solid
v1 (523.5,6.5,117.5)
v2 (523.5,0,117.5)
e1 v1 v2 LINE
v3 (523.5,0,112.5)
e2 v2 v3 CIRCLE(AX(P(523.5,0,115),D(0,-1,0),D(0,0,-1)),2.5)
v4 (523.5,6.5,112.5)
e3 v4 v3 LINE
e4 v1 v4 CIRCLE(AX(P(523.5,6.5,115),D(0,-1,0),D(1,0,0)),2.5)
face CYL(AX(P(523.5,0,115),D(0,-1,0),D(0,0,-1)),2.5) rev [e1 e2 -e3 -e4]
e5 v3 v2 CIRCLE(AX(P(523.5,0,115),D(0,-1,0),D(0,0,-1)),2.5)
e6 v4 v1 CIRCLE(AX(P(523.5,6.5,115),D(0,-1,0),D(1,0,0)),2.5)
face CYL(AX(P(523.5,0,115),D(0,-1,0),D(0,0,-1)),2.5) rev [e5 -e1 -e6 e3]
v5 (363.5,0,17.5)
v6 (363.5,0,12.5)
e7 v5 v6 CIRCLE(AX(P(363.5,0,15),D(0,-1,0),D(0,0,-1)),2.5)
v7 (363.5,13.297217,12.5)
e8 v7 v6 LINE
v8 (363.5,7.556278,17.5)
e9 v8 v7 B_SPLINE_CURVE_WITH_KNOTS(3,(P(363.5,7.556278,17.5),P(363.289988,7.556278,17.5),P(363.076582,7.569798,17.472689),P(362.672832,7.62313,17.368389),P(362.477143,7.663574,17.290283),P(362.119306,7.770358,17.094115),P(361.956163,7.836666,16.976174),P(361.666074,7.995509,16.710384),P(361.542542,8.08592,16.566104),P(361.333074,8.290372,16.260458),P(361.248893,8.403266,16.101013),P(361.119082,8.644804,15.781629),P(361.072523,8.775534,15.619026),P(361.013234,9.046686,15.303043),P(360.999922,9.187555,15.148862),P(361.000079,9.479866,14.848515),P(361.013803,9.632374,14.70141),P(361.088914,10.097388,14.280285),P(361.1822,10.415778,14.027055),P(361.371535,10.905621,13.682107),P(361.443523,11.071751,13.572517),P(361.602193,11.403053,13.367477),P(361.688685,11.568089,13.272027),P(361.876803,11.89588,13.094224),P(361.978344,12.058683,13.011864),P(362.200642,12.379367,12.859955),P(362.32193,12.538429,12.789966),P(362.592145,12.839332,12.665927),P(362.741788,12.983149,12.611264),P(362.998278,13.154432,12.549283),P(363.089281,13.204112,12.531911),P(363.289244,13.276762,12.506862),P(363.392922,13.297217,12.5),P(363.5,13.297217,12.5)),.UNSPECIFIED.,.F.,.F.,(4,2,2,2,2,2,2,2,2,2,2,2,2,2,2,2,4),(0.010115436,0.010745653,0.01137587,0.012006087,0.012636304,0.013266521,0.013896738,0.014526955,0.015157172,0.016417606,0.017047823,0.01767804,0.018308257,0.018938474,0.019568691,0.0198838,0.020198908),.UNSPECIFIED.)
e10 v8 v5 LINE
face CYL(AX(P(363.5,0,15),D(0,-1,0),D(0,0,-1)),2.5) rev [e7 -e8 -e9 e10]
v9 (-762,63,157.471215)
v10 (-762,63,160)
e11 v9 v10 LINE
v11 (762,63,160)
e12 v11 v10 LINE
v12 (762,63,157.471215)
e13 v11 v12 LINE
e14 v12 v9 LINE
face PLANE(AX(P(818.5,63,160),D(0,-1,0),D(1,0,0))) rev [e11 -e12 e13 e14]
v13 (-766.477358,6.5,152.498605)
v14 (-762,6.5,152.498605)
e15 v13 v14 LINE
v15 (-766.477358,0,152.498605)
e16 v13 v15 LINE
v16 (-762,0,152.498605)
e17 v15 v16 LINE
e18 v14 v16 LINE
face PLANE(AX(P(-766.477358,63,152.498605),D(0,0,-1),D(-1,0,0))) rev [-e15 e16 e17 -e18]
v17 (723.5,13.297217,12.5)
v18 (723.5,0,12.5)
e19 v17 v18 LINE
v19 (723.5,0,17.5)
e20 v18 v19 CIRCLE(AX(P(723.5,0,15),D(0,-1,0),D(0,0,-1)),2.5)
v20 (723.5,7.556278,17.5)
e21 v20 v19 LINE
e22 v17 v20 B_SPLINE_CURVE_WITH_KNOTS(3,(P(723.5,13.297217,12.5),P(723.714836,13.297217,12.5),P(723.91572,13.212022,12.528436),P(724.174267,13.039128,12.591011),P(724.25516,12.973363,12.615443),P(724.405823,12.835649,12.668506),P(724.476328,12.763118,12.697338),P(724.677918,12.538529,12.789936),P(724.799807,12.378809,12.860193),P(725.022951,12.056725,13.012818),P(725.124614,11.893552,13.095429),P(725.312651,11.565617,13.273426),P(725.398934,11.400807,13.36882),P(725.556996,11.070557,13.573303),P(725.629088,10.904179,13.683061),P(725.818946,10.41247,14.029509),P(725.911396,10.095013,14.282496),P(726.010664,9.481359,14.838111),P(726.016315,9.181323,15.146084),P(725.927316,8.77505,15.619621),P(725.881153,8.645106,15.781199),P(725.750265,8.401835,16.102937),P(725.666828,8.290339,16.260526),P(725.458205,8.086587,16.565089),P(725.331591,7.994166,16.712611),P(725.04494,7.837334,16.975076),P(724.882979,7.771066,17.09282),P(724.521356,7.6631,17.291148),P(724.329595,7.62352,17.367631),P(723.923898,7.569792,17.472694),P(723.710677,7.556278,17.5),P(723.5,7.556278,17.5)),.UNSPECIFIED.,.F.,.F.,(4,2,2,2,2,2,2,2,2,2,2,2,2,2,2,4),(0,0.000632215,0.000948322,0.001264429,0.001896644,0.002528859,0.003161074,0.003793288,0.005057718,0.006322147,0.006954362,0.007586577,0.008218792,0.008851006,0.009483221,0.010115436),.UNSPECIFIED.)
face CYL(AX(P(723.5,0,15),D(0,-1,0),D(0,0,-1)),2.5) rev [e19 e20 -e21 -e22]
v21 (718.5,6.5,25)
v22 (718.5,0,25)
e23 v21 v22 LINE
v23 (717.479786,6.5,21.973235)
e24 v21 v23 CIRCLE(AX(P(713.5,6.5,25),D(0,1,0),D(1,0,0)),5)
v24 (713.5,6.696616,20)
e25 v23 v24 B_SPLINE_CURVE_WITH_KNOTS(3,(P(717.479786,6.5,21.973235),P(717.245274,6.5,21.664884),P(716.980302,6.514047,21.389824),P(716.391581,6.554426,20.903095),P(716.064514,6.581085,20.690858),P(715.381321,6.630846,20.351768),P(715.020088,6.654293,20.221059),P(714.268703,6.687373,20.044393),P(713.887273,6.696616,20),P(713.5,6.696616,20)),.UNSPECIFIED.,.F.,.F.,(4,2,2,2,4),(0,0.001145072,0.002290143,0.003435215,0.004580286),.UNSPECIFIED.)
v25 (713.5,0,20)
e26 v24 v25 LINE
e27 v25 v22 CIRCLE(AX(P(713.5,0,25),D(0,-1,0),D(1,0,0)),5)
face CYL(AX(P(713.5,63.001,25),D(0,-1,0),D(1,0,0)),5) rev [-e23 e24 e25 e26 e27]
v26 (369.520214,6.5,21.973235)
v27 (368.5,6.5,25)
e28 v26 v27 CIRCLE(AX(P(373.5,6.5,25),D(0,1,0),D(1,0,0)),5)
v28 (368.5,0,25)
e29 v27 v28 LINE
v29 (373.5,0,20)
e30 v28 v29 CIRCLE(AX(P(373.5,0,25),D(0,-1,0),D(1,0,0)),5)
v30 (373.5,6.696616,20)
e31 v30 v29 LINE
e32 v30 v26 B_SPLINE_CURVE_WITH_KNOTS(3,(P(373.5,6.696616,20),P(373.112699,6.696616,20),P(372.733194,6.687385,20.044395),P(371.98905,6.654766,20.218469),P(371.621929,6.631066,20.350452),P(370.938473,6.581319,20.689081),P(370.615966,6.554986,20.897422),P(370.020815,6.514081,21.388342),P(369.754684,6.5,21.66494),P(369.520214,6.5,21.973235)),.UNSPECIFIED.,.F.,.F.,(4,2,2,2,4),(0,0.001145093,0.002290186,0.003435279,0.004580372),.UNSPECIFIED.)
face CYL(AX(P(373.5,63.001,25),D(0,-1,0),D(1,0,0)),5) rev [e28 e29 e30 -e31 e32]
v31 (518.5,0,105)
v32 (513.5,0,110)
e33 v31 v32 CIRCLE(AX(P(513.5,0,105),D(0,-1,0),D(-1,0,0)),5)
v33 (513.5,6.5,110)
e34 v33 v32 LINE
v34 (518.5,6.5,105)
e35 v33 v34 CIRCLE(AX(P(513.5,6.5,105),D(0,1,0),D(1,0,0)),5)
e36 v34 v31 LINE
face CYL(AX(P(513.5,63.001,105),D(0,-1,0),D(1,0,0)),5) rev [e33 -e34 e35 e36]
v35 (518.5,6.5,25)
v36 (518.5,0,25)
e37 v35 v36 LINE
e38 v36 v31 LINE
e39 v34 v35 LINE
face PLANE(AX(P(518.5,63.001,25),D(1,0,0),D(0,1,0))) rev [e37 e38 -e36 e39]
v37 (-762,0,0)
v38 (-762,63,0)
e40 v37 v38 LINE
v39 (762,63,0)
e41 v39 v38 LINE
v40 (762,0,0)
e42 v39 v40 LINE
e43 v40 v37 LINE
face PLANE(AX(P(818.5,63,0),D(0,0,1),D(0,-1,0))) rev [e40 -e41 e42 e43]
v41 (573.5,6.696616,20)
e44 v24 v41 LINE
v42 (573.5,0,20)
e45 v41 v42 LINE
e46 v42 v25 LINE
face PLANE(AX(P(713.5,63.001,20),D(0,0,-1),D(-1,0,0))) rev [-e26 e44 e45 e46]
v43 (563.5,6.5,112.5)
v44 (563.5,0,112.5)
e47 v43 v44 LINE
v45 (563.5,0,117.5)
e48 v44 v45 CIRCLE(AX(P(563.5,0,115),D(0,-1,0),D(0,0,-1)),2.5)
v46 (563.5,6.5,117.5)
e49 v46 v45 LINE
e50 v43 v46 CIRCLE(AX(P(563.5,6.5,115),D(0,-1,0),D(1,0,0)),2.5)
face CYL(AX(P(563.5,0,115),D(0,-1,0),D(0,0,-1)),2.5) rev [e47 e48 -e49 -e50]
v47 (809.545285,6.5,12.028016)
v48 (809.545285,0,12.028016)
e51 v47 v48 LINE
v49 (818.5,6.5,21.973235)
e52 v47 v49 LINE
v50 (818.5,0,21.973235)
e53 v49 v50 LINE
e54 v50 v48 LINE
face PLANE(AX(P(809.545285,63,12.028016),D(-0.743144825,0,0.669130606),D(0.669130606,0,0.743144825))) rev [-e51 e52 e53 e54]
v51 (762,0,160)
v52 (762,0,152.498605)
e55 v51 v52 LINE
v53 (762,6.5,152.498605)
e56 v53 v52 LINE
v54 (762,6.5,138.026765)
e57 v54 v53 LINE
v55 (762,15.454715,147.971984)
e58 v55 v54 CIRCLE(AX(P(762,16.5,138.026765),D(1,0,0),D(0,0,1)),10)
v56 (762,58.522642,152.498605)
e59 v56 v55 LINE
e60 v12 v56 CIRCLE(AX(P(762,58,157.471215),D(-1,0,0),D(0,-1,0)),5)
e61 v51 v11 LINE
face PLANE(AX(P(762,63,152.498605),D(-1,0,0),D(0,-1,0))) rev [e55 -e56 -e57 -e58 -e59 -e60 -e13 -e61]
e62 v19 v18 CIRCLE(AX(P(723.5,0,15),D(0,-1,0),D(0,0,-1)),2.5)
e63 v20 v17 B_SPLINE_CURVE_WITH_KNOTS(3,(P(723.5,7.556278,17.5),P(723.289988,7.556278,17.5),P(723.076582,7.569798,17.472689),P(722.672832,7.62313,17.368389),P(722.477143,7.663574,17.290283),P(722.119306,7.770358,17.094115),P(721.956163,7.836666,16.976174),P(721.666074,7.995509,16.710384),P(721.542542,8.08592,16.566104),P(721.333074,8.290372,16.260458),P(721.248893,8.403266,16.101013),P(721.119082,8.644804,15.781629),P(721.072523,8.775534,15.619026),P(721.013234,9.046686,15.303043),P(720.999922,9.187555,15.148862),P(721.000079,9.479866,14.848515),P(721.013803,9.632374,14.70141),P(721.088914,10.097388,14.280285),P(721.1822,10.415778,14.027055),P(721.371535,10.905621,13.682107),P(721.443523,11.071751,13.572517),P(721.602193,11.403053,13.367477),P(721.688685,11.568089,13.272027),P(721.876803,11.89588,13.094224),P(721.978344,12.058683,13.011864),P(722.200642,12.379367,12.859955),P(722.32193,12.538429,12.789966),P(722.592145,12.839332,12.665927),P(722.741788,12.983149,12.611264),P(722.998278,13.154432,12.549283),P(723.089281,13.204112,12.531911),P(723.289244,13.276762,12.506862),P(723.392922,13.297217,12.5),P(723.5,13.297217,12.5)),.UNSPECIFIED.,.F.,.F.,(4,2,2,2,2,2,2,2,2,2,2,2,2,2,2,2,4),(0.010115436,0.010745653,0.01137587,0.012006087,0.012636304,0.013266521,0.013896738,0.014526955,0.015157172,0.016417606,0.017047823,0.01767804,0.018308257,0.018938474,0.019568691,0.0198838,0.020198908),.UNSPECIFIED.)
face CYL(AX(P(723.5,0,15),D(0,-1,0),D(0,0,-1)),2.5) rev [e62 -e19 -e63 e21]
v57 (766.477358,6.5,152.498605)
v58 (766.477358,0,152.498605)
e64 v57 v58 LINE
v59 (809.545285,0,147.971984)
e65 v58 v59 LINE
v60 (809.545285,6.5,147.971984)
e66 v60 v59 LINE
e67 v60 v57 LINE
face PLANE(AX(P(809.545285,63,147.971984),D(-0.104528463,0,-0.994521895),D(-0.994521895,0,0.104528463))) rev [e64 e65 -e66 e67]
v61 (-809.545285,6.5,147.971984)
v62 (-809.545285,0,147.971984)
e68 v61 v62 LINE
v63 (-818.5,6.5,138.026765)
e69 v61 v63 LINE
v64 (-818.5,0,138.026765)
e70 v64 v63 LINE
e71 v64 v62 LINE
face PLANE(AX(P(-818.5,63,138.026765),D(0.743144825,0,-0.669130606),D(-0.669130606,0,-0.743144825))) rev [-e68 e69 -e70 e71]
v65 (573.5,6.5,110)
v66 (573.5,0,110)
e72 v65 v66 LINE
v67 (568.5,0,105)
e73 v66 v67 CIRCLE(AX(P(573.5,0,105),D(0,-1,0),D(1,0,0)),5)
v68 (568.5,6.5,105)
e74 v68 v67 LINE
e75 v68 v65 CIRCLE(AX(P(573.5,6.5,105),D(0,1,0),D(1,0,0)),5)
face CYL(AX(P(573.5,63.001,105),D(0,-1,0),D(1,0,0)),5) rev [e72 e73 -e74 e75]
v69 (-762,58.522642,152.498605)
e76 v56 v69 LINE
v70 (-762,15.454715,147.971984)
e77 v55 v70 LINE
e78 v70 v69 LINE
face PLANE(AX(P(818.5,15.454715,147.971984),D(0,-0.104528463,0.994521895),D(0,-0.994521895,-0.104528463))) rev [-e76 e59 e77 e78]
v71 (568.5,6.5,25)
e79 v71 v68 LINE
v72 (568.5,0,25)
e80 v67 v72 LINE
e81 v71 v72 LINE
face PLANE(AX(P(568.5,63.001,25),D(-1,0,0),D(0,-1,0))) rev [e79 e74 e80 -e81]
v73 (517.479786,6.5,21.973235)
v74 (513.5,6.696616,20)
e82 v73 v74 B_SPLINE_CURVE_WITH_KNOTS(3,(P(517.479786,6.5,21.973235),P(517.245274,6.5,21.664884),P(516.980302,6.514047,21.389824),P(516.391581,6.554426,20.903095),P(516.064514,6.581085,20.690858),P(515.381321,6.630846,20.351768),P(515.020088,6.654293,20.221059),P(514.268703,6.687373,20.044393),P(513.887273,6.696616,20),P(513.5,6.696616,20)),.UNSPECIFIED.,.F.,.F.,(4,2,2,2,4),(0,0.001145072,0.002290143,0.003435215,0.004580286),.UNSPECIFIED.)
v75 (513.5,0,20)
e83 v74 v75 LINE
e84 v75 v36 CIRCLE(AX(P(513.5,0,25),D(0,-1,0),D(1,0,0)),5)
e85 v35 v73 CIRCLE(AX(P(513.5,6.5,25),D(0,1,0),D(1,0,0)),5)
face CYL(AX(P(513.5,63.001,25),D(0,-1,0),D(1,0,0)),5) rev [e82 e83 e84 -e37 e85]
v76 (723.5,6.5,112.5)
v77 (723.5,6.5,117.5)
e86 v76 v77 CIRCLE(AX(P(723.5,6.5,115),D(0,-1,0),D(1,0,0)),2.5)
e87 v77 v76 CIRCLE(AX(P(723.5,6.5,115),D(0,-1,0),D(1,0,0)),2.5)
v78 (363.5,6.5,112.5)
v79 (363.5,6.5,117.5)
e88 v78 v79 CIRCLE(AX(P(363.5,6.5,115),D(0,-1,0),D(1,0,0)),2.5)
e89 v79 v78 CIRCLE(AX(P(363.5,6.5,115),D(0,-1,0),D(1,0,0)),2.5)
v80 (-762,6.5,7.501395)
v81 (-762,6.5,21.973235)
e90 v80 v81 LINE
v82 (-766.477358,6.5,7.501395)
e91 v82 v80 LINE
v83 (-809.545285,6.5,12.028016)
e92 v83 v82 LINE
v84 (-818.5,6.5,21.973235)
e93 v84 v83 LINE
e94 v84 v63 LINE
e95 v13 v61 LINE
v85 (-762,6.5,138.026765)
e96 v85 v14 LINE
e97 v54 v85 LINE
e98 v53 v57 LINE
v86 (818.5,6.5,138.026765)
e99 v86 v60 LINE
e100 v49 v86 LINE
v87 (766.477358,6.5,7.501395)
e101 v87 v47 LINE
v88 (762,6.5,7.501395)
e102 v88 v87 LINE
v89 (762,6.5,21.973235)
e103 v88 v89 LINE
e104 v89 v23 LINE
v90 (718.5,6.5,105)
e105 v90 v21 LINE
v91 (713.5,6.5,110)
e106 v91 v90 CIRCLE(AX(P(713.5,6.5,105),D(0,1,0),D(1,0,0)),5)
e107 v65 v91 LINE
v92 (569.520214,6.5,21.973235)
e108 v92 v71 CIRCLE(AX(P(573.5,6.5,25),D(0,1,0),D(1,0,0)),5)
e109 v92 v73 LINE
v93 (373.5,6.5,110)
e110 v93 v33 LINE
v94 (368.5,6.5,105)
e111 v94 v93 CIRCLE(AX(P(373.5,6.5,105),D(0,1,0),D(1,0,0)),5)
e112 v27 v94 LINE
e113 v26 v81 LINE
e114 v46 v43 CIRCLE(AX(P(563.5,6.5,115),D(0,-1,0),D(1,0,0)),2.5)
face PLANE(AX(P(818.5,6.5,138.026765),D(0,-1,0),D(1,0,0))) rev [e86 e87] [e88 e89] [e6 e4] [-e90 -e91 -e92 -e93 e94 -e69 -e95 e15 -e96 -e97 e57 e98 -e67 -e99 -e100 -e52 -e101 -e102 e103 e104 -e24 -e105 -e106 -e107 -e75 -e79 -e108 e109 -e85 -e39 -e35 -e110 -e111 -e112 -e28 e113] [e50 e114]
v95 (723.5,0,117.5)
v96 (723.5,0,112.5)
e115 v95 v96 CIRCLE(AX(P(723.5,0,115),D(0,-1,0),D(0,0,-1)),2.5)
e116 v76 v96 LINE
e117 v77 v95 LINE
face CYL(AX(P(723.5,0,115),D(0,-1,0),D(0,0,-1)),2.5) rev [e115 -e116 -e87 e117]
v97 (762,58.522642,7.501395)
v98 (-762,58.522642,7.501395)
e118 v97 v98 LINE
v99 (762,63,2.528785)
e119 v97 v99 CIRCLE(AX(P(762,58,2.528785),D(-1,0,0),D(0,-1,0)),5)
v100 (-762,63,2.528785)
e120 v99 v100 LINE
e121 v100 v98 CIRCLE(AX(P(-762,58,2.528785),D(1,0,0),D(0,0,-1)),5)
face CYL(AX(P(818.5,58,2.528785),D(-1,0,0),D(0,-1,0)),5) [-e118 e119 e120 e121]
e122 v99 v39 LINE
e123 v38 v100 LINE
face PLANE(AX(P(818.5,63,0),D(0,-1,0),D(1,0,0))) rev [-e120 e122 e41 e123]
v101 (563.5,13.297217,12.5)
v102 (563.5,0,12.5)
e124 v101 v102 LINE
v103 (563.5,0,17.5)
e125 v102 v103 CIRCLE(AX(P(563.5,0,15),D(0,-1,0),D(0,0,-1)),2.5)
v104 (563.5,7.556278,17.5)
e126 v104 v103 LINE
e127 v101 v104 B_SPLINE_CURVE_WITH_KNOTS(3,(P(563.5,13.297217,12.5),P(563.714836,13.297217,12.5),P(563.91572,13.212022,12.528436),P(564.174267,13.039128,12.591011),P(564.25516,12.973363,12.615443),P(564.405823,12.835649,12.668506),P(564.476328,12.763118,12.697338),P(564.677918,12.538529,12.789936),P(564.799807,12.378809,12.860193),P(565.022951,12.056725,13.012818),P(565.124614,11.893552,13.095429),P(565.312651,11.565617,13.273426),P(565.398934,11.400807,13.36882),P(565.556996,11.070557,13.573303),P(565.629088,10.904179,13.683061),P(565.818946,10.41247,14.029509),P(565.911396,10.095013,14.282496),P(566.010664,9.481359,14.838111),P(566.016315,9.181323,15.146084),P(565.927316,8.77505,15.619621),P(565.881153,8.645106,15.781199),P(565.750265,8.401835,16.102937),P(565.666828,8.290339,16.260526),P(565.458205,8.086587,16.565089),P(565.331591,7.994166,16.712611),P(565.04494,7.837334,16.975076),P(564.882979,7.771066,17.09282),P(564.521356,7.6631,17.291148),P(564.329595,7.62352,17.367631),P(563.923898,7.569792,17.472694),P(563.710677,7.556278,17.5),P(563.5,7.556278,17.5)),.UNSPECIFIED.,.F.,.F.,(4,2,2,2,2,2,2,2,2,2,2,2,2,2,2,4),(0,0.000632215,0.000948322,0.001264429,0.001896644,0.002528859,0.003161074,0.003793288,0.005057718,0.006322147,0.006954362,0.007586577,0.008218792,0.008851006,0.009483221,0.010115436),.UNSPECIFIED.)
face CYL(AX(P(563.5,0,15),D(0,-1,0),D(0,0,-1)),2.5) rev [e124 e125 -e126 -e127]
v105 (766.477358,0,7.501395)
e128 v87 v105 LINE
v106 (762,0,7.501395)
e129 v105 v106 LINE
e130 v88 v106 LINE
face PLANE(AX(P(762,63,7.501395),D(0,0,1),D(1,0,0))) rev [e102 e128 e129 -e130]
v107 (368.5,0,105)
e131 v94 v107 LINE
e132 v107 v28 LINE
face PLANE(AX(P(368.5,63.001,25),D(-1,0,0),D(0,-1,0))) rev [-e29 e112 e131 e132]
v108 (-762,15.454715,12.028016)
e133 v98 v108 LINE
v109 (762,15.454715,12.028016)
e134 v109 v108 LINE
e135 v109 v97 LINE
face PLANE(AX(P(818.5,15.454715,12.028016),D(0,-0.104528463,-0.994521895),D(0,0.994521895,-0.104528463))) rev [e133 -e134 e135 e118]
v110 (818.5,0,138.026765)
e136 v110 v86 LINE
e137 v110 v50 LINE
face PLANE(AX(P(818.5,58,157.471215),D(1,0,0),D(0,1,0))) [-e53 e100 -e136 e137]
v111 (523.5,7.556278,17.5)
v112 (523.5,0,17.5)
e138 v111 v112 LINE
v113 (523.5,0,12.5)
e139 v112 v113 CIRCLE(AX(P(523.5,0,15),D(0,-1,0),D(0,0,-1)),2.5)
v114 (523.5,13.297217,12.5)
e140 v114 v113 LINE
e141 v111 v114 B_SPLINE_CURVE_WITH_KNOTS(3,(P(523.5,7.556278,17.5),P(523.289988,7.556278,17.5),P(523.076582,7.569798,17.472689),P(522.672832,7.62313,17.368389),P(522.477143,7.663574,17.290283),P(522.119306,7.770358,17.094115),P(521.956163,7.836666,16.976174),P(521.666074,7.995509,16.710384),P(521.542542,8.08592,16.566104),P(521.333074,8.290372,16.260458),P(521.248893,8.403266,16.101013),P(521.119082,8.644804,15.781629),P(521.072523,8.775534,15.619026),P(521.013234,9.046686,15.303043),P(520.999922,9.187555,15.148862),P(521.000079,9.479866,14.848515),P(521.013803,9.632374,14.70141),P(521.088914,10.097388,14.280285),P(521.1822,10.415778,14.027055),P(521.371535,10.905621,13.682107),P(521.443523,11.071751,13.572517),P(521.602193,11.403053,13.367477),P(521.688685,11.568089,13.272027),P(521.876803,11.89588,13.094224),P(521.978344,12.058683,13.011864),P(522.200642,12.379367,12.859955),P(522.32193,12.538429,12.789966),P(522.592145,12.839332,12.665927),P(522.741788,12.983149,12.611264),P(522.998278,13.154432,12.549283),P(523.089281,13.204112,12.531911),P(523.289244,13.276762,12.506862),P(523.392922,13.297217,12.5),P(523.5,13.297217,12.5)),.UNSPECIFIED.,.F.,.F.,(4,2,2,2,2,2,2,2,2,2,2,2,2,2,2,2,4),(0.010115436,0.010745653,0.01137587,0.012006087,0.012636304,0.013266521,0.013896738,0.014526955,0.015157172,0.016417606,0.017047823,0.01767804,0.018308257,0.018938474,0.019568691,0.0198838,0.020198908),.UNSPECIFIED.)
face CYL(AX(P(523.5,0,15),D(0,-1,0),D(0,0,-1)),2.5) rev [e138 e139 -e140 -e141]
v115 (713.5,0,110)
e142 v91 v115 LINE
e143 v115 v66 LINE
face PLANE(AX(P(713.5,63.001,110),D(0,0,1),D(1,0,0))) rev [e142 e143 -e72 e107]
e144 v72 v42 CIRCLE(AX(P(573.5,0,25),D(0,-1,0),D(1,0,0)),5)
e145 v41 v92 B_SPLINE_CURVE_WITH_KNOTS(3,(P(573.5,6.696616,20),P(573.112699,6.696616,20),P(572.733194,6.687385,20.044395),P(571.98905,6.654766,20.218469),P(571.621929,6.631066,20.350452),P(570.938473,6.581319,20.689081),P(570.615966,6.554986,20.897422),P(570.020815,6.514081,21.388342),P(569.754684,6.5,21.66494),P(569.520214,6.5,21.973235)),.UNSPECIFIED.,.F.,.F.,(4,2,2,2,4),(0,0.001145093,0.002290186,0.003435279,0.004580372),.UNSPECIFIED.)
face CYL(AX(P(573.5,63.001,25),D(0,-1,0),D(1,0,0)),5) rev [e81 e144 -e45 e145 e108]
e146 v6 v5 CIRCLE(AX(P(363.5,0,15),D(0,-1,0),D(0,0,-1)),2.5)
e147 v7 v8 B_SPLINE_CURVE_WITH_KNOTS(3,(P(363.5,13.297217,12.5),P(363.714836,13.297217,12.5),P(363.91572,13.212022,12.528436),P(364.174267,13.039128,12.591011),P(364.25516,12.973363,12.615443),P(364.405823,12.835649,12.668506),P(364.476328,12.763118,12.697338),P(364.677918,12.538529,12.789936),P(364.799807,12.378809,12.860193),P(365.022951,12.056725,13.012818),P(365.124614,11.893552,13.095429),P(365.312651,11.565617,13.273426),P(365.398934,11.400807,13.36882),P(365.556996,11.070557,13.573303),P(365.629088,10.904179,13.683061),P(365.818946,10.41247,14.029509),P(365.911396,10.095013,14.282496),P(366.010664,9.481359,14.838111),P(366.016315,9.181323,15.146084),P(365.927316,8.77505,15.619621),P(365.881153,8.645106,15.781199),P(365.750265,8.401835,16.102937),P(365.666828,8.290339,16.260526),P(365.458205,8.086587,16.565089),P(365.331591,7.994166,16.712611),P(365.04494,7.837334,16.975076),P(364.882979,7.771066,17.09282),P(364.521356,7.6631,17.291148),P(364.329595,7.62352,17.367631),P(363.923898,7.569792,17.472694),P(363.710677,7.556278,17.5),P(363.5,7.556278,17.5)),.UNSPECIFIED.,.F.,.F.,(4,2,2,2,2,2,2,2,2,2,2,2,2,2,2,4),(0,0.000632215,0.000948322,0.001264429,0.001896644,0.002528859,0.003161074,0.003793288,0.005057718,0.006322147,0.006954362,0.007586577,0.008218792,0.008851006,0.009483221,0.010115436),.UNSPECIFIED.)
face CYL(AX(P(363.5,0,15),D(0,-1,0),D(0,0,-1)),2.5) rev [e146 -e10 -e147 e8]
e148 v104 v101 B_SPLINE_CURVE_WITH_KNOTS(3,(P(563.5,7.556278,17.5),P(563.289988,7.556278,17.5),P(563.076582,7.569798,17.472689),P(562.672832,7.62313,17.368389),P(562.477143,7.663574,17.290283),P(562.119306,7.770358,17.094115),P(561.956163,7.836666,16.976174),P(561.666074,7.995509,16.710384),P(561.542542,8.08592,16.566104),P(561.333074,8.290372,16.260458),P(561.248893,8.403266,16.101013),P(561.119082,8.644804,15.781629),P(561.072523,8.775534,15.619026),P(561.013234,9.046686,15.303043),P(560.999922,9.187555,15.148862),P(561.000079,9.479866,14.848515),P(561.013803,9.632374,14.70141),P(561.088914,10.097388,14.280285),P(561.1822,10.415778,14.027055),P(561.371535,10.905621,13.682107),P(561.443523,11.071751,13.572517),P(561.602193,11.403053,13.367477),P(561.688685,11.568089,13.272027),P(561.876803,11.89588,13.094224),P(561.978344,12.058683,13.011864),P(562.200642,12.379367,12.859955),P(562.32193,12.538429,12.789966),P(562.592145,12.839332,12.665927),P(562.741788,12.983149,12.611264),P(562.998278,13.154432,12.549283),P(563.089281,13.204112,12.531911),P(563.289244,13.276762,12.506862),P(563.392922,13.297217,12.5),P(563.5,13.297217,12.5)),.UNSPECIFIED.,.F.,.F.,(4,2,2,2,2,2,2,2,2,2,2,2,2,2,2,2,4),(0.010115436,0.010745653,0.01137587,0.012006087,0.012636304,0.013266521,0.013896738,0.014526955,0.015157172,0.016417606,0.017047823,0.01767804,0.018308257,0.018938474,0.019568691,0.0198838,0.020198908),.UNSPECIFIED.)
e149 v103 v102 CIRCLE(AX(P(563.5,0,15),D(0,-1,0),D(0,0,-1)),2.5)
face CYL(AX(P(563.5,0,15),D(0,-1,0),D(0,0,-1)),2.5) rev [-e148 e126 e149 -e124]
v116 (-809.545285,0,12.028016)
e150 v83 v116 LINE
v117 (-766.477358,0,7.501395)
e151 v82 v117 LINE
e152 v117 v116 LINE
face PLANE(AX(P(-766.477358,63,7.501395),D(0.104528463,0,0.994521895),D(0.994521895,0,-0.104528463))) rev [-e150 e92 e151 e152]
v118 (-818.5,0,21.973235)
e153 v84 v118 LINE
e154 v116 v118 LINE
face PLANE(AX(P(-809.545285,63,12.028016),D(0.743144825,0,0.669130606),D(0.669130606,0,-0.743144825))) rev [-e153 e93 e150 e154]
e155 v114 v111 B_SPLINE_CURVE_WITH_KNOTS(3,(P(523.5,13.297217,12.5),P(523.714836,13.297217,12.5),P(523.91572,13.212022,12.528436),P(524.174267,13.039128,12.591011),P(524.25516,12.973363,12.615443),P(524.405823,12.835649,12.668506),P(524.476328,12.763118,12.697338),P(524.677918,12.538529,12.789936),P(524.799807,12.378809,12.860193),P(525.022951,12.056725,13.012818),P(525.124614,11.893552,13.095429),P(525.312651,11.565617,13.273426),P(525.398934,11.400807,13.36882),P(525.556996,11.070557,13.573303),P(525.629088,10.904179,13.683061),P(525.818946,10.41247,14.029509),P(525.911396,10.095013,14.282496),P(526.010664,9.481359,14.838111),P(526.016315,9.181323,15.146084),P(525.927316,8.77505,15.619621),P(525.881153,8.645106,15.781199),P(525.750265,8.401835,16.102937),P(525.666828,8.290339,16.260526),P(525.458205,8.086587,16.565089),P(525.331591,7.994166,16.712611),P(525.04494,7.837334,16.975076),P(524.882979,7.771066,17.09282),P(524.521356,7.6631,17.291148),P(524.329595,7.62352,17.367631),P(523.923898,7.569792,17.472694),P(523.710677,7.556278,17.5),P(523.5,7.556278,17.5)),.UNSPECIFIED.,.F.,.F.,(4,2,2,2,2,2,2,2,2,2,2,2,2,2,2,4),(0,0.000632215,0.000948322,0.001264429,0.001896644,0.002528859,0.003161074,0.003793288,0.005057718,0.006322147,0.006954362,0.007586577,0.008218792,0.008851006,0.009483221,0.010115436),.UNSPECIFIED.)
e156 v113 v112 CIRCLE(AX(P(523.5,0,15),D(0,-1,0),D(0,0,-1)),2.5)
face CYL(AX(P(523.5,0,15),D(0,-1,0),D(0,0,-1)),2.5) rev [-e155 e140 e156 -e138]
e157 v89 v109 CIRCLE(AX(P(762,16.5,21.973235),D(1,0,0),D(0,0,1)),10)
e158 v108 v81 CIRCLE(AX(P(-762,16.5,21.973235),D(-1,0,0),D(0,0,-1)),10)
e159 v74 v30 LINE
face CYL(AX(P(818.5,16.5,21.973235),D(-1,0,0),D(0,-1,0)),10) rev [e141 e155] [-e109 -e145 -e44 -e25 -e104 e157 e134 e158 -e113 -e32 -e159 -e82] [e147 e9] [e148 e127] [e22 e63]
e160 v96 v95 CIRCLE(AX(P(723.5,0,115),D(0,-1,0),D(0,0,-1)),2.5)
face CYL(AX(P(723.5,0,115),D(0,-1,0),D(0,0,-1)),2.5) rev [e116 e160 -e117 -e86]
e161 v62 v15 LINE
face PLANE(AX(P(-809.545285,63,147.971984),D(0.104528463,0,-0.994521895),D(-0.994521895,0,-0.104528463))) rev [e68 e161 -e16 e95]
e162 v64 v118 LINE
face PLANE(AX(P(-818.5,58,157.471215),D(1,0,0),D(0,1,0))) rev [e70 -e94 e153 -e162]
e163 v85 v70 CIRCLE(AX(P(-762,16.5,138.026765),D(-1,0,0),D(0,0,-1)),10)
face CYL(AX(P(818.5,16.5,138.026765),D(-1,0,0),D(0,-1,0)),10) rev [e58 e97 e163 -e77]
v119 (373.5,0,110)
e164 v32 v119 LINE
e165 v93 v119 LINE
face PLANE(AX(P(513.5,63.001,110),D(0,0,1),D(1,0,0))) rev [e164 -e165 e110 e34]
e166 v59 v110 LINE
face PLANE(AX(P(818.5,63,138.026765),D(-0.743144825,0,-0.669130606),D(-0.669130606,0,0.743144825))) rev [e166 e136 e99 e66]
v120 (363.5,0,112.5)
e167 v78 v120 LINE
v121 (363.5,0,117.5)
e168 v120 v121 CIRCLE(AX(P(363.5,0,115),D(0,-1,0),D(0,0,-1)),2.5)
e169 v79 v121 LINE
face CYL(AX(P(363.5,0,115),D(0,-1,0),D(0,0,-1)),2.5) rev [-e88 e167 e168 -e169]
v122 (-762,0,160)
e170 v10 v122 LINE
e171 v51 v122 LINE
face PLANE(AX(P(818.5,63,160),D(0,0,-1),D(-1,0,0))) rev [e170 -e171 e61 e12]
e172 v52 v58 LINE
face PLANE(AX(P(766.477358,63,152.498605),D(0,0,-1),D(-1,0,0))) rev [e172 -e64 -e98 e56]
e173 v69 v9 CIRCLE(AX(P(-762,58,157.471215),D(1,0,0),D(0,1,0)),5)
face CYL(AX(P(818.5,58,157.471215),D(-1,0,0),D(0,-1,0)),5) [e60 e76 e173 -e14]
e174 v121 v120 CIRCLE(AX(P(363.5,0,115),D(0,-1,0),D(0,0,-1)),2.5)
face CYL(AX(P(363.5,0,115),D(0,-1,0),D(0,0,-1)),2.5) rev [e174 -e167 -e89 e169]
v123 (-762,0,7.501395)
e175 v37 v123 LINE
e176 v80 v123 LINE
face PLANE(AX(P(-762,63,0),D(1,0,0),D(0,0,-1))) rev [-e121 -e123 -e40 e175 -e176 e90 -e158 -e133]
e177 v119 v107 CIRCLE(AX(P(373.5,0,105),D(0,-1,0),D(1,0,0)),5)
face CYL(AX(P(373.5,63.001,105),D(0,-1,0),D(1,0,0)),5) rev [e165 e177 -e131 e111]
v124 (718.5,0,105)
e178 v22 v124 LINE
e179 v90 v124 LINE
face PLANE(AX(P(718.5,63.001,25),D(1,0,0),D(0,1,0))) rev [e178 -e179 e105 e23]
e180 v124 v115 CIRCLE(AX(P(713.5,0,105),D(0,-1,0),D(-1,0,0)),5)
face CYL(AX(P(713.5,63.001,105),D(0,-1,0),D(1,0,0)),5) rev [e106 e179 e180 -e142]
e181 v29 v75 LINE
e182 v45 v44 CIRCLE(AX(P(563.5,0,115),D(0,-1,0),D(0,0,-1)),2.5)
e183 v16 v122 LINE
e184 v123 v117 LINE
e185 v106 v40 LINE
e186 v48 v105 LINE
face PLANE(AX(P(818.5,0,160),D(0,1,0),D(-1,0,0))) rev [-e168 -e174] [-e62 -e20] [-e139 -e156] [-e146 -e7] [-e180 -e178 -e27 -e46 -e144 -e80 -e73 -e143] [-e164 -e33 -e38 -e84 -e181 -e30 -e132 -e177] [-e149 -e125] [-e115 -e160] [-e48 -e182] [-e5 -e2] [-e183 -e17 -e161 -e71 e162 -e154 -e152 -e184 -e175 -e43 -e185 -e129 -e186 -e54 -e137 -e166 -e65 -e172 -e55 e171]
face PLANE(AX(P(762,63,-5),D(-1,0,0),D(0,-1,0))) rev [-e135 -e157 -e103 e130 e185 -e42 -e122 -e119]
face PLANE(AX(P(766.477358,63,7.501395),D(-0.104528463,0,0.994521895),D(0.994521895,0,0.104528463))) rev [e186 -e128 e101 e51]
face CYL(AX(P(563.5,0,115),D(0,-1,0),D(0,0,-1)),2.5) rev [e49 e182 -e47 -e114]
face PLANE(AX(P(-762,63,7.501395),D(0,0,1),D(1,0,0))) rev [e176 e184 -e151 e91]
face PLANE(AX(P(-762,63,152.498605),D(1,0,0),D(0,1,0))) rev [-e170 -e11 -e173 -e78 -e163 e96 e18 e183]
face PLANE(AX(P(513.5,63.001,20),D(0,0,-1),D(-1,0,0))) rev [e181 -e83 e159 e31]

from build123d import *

# Parameters (mm, degrees)
GBT706_2008_16A_1_DEPTH = 1637
CUT_EXTRUDE_1_DEPTH     = 837.367891541
CUT_EXTRUDE_2_DEPTH     = 837.367891541
SKETCH_4_W              = 56.5
SKETCH_4_H              = 56.5
CUT_EXTRUDE_3_DEPTH     = 835.965313439
SKETCH_5_W              = 56.5
SKETCH_5_H              = 56.5
CUT_EXTRUDE_4_DEPTH     = 835.965313439
CUT_EXTRUDE_5_REACH     = 838.368
HOLE_WIZARD_M6_1_D      = 5


with BuildPart() as part:
    # Sketch12 → Gbt706-2008 热轧槽钢 16A(1) (new body)
    with BuildSketch(Plane.YZ.offset(-818.5)):
        with BuildLine():
            Line((63, 160), (0, 160))
            Line((0, 160), (0, 0))
            Line((0, 0), (63, 0))
            Line((63, 0), (63, 2.528785132))
            ThreePointArc((63, 2.528785132), (61.715724127, 5.874438164), (58.522642316, 7.501394609))
            Line((58.522642316, 7.501394609), (15.454715367, 12.028016136))
            ThreePointArc((15.454715367, 12.028016136), (9.068551745, 15.281929026), (6.5, 21.973235089))
            Line((6.5, 21.973235089), (6.5, 138.026764911))
            ThreePointArc((6.5, 138.026764911), (9.068551745, 144.718070974), (15.454715367, 147.971983864))
            Line((15.454715367, 147.971983864), (58.522642316, 152.498605391))
            ThreePointArc((58.522642316, 152.498605391), (61.715724127, 154.125561836), (63, 157.471214868))
            Line((63, 157.471214868), (63, 160))
        make_face()
    extrude(amount=GBT706_2008_16A_1_DEPTH)

    # 草图2 → 切除-拉伸1 (cut, through all)
    with BuildSketch(Plane.XZ):
        Polygon((762, -5), (762, 7.501394609), (766.477357684, 7.501394609), (809.545284633, 12.028016136), (818.5, 21.973235089), (818.5, 138.026764911), (809.545284633, 147.971983864), (766.477357684, 152.498605391), (762, 152.498605391), (762, 165), (828.5, 165), (828.5, -5), align=None)
    extrude(amount=-CUT_EXTRUDE_1_DEPTH, mode=Mode.SUBTRACT)

    # 草图3 → 切除-拉伸2 (cut, through all)
    with BuildSketch(Plane.XZ):
        Polygon((-762, 0), (-762, 7.501394609), (-766.477357684, 7.501394609), (-809.545284633, 12.028016136), (-818.5, 21.973235089), (-818.5, 138.026764911), (-809.545284633, 147.971983864), (-766.477357684, 152.498605391), (-762, 152.498605391), (-762, 165), (-838.5, 165), (-838.5, -5), (-762, -5), align=None)
    extrude(amount=-CUT_EXTRUDE_2_DEPTH, mode=Mode.SUBTRACT)

    # 草图4 → 切除-拉伸3 (cut, through all)
    with BuildSketch(Plane.XY.offset(152.498605391)):
        with Locations((790.25, 34.75)):
            Rectangle(SKETCH_4_W, SKETCH_4_H)
    extrude(amount=-CUT_EXTRUDE_3_DEPTH, mode=Mode.SUBTRACT)

    # 草图5 → 切除-拉伸4 (cut, through all)
    with BuildSketch(Plane.XY.offset(152.498605391)):
        with Locations((-790.25, 34.75)):
            Rectangle(SKETCH_5_W, SKETCH_5_H)
    extrude(amount=-CUT_EXTRUDE_4_DEPTH, mode=Mode.SUBTRACT)

    # 草图6 → 切除-拉伸5 (cut, up to next)
    with BuildSketch(Plane.XZ, mode=Mode.PRIVATE) as cut_extrude_5_sk1:
        with BuildLine():
            Line((513.5, 20), (373.5, 20))
            ThreePointArc((373.5, 20), (369.964466094, 21.464466094), (368.5, 25))
            Line((368.5, 25), (368.5, 105))
            ThreePointArc((368.5, 105), (369.964466094, 108.535533906), (373.5, 110))
            Line((373.5, 110), (513.5, 110))
            ThreePointArc((513.5, 110), (517.035533906, 108.535533906), (518.5, 105))
            Line((518.5, 105), (518.5, 25))
            ThreePointArc((518.5, 25), (517.035533906, 21.464466094), (513.5, 20))
        make_face()
    cut_extrude_5_tool1 = extrude(cut_extrude_5_sk1.sketch, amount=-CUT_EXTRUDE_5_REACH, mode=Mode.PRIVATE) & part.part
    # 草图6 → 切除-拉伸5 (cut, up to next)
    with BuildSketch(Plane.XZ, mode=Mode.PRIVATE) as cut_extrude_5_sk2:
        with BuildLine():
            Line((718.5, 25), (718.5, 105))
            ThreePointArc((718.5, 105), (717.035533906, 108.535533906), (713.5, 110))
            Line((713.5, 110), (573.5, 110))
            ThreePointArc((573.5, 110), (569.964466094, 108.535533906), (568.5, 105))
            Line((568.5, 105), (568.5, 25))
            ThreePointArc((568.5, 25), (569.964466094, 21.464466094), (573.5, 20))
            Line((573.5, 20), (713.5, 20))
            ThreePointArc((713.5, 20), (717.035533906, 21.464466094), (718.5, 25))
        make_face()
    cut_extrude_5_tool2 = extrude(cut_extrude_5_sk2.sketch, amount=-CUT_EXTRUDE_5_REACH, mode=Mode.PRIVATE) & part.part
    add(cut_extrude_5_tool1.solids().sort_by_distance((443.5, 0, 65))[0], mode=Mode.SUBTRACT)
    add(cut_extrude_5_tool2.solids().sort_by_distance((643.5, 0, 65))[0], mode=Mode.SUBTRACT)

    # M6 螺纹孔1 (through all)
    with Locations(Plane(origin=(0, 0, 0), x_dir=(-1, 0, 0), z_dir=(0, -1, 0))):
        with Locations((-723.5, -15), (-523.5, -15), (-563.5, -15), (-363.5, -15), (-563.5, -115), (-363.5, -115), (-723.5, -115), (-523.5, -115)):
            Hole(HOLE_WIZARD_M6_1_D / 2)


solid = part.part
